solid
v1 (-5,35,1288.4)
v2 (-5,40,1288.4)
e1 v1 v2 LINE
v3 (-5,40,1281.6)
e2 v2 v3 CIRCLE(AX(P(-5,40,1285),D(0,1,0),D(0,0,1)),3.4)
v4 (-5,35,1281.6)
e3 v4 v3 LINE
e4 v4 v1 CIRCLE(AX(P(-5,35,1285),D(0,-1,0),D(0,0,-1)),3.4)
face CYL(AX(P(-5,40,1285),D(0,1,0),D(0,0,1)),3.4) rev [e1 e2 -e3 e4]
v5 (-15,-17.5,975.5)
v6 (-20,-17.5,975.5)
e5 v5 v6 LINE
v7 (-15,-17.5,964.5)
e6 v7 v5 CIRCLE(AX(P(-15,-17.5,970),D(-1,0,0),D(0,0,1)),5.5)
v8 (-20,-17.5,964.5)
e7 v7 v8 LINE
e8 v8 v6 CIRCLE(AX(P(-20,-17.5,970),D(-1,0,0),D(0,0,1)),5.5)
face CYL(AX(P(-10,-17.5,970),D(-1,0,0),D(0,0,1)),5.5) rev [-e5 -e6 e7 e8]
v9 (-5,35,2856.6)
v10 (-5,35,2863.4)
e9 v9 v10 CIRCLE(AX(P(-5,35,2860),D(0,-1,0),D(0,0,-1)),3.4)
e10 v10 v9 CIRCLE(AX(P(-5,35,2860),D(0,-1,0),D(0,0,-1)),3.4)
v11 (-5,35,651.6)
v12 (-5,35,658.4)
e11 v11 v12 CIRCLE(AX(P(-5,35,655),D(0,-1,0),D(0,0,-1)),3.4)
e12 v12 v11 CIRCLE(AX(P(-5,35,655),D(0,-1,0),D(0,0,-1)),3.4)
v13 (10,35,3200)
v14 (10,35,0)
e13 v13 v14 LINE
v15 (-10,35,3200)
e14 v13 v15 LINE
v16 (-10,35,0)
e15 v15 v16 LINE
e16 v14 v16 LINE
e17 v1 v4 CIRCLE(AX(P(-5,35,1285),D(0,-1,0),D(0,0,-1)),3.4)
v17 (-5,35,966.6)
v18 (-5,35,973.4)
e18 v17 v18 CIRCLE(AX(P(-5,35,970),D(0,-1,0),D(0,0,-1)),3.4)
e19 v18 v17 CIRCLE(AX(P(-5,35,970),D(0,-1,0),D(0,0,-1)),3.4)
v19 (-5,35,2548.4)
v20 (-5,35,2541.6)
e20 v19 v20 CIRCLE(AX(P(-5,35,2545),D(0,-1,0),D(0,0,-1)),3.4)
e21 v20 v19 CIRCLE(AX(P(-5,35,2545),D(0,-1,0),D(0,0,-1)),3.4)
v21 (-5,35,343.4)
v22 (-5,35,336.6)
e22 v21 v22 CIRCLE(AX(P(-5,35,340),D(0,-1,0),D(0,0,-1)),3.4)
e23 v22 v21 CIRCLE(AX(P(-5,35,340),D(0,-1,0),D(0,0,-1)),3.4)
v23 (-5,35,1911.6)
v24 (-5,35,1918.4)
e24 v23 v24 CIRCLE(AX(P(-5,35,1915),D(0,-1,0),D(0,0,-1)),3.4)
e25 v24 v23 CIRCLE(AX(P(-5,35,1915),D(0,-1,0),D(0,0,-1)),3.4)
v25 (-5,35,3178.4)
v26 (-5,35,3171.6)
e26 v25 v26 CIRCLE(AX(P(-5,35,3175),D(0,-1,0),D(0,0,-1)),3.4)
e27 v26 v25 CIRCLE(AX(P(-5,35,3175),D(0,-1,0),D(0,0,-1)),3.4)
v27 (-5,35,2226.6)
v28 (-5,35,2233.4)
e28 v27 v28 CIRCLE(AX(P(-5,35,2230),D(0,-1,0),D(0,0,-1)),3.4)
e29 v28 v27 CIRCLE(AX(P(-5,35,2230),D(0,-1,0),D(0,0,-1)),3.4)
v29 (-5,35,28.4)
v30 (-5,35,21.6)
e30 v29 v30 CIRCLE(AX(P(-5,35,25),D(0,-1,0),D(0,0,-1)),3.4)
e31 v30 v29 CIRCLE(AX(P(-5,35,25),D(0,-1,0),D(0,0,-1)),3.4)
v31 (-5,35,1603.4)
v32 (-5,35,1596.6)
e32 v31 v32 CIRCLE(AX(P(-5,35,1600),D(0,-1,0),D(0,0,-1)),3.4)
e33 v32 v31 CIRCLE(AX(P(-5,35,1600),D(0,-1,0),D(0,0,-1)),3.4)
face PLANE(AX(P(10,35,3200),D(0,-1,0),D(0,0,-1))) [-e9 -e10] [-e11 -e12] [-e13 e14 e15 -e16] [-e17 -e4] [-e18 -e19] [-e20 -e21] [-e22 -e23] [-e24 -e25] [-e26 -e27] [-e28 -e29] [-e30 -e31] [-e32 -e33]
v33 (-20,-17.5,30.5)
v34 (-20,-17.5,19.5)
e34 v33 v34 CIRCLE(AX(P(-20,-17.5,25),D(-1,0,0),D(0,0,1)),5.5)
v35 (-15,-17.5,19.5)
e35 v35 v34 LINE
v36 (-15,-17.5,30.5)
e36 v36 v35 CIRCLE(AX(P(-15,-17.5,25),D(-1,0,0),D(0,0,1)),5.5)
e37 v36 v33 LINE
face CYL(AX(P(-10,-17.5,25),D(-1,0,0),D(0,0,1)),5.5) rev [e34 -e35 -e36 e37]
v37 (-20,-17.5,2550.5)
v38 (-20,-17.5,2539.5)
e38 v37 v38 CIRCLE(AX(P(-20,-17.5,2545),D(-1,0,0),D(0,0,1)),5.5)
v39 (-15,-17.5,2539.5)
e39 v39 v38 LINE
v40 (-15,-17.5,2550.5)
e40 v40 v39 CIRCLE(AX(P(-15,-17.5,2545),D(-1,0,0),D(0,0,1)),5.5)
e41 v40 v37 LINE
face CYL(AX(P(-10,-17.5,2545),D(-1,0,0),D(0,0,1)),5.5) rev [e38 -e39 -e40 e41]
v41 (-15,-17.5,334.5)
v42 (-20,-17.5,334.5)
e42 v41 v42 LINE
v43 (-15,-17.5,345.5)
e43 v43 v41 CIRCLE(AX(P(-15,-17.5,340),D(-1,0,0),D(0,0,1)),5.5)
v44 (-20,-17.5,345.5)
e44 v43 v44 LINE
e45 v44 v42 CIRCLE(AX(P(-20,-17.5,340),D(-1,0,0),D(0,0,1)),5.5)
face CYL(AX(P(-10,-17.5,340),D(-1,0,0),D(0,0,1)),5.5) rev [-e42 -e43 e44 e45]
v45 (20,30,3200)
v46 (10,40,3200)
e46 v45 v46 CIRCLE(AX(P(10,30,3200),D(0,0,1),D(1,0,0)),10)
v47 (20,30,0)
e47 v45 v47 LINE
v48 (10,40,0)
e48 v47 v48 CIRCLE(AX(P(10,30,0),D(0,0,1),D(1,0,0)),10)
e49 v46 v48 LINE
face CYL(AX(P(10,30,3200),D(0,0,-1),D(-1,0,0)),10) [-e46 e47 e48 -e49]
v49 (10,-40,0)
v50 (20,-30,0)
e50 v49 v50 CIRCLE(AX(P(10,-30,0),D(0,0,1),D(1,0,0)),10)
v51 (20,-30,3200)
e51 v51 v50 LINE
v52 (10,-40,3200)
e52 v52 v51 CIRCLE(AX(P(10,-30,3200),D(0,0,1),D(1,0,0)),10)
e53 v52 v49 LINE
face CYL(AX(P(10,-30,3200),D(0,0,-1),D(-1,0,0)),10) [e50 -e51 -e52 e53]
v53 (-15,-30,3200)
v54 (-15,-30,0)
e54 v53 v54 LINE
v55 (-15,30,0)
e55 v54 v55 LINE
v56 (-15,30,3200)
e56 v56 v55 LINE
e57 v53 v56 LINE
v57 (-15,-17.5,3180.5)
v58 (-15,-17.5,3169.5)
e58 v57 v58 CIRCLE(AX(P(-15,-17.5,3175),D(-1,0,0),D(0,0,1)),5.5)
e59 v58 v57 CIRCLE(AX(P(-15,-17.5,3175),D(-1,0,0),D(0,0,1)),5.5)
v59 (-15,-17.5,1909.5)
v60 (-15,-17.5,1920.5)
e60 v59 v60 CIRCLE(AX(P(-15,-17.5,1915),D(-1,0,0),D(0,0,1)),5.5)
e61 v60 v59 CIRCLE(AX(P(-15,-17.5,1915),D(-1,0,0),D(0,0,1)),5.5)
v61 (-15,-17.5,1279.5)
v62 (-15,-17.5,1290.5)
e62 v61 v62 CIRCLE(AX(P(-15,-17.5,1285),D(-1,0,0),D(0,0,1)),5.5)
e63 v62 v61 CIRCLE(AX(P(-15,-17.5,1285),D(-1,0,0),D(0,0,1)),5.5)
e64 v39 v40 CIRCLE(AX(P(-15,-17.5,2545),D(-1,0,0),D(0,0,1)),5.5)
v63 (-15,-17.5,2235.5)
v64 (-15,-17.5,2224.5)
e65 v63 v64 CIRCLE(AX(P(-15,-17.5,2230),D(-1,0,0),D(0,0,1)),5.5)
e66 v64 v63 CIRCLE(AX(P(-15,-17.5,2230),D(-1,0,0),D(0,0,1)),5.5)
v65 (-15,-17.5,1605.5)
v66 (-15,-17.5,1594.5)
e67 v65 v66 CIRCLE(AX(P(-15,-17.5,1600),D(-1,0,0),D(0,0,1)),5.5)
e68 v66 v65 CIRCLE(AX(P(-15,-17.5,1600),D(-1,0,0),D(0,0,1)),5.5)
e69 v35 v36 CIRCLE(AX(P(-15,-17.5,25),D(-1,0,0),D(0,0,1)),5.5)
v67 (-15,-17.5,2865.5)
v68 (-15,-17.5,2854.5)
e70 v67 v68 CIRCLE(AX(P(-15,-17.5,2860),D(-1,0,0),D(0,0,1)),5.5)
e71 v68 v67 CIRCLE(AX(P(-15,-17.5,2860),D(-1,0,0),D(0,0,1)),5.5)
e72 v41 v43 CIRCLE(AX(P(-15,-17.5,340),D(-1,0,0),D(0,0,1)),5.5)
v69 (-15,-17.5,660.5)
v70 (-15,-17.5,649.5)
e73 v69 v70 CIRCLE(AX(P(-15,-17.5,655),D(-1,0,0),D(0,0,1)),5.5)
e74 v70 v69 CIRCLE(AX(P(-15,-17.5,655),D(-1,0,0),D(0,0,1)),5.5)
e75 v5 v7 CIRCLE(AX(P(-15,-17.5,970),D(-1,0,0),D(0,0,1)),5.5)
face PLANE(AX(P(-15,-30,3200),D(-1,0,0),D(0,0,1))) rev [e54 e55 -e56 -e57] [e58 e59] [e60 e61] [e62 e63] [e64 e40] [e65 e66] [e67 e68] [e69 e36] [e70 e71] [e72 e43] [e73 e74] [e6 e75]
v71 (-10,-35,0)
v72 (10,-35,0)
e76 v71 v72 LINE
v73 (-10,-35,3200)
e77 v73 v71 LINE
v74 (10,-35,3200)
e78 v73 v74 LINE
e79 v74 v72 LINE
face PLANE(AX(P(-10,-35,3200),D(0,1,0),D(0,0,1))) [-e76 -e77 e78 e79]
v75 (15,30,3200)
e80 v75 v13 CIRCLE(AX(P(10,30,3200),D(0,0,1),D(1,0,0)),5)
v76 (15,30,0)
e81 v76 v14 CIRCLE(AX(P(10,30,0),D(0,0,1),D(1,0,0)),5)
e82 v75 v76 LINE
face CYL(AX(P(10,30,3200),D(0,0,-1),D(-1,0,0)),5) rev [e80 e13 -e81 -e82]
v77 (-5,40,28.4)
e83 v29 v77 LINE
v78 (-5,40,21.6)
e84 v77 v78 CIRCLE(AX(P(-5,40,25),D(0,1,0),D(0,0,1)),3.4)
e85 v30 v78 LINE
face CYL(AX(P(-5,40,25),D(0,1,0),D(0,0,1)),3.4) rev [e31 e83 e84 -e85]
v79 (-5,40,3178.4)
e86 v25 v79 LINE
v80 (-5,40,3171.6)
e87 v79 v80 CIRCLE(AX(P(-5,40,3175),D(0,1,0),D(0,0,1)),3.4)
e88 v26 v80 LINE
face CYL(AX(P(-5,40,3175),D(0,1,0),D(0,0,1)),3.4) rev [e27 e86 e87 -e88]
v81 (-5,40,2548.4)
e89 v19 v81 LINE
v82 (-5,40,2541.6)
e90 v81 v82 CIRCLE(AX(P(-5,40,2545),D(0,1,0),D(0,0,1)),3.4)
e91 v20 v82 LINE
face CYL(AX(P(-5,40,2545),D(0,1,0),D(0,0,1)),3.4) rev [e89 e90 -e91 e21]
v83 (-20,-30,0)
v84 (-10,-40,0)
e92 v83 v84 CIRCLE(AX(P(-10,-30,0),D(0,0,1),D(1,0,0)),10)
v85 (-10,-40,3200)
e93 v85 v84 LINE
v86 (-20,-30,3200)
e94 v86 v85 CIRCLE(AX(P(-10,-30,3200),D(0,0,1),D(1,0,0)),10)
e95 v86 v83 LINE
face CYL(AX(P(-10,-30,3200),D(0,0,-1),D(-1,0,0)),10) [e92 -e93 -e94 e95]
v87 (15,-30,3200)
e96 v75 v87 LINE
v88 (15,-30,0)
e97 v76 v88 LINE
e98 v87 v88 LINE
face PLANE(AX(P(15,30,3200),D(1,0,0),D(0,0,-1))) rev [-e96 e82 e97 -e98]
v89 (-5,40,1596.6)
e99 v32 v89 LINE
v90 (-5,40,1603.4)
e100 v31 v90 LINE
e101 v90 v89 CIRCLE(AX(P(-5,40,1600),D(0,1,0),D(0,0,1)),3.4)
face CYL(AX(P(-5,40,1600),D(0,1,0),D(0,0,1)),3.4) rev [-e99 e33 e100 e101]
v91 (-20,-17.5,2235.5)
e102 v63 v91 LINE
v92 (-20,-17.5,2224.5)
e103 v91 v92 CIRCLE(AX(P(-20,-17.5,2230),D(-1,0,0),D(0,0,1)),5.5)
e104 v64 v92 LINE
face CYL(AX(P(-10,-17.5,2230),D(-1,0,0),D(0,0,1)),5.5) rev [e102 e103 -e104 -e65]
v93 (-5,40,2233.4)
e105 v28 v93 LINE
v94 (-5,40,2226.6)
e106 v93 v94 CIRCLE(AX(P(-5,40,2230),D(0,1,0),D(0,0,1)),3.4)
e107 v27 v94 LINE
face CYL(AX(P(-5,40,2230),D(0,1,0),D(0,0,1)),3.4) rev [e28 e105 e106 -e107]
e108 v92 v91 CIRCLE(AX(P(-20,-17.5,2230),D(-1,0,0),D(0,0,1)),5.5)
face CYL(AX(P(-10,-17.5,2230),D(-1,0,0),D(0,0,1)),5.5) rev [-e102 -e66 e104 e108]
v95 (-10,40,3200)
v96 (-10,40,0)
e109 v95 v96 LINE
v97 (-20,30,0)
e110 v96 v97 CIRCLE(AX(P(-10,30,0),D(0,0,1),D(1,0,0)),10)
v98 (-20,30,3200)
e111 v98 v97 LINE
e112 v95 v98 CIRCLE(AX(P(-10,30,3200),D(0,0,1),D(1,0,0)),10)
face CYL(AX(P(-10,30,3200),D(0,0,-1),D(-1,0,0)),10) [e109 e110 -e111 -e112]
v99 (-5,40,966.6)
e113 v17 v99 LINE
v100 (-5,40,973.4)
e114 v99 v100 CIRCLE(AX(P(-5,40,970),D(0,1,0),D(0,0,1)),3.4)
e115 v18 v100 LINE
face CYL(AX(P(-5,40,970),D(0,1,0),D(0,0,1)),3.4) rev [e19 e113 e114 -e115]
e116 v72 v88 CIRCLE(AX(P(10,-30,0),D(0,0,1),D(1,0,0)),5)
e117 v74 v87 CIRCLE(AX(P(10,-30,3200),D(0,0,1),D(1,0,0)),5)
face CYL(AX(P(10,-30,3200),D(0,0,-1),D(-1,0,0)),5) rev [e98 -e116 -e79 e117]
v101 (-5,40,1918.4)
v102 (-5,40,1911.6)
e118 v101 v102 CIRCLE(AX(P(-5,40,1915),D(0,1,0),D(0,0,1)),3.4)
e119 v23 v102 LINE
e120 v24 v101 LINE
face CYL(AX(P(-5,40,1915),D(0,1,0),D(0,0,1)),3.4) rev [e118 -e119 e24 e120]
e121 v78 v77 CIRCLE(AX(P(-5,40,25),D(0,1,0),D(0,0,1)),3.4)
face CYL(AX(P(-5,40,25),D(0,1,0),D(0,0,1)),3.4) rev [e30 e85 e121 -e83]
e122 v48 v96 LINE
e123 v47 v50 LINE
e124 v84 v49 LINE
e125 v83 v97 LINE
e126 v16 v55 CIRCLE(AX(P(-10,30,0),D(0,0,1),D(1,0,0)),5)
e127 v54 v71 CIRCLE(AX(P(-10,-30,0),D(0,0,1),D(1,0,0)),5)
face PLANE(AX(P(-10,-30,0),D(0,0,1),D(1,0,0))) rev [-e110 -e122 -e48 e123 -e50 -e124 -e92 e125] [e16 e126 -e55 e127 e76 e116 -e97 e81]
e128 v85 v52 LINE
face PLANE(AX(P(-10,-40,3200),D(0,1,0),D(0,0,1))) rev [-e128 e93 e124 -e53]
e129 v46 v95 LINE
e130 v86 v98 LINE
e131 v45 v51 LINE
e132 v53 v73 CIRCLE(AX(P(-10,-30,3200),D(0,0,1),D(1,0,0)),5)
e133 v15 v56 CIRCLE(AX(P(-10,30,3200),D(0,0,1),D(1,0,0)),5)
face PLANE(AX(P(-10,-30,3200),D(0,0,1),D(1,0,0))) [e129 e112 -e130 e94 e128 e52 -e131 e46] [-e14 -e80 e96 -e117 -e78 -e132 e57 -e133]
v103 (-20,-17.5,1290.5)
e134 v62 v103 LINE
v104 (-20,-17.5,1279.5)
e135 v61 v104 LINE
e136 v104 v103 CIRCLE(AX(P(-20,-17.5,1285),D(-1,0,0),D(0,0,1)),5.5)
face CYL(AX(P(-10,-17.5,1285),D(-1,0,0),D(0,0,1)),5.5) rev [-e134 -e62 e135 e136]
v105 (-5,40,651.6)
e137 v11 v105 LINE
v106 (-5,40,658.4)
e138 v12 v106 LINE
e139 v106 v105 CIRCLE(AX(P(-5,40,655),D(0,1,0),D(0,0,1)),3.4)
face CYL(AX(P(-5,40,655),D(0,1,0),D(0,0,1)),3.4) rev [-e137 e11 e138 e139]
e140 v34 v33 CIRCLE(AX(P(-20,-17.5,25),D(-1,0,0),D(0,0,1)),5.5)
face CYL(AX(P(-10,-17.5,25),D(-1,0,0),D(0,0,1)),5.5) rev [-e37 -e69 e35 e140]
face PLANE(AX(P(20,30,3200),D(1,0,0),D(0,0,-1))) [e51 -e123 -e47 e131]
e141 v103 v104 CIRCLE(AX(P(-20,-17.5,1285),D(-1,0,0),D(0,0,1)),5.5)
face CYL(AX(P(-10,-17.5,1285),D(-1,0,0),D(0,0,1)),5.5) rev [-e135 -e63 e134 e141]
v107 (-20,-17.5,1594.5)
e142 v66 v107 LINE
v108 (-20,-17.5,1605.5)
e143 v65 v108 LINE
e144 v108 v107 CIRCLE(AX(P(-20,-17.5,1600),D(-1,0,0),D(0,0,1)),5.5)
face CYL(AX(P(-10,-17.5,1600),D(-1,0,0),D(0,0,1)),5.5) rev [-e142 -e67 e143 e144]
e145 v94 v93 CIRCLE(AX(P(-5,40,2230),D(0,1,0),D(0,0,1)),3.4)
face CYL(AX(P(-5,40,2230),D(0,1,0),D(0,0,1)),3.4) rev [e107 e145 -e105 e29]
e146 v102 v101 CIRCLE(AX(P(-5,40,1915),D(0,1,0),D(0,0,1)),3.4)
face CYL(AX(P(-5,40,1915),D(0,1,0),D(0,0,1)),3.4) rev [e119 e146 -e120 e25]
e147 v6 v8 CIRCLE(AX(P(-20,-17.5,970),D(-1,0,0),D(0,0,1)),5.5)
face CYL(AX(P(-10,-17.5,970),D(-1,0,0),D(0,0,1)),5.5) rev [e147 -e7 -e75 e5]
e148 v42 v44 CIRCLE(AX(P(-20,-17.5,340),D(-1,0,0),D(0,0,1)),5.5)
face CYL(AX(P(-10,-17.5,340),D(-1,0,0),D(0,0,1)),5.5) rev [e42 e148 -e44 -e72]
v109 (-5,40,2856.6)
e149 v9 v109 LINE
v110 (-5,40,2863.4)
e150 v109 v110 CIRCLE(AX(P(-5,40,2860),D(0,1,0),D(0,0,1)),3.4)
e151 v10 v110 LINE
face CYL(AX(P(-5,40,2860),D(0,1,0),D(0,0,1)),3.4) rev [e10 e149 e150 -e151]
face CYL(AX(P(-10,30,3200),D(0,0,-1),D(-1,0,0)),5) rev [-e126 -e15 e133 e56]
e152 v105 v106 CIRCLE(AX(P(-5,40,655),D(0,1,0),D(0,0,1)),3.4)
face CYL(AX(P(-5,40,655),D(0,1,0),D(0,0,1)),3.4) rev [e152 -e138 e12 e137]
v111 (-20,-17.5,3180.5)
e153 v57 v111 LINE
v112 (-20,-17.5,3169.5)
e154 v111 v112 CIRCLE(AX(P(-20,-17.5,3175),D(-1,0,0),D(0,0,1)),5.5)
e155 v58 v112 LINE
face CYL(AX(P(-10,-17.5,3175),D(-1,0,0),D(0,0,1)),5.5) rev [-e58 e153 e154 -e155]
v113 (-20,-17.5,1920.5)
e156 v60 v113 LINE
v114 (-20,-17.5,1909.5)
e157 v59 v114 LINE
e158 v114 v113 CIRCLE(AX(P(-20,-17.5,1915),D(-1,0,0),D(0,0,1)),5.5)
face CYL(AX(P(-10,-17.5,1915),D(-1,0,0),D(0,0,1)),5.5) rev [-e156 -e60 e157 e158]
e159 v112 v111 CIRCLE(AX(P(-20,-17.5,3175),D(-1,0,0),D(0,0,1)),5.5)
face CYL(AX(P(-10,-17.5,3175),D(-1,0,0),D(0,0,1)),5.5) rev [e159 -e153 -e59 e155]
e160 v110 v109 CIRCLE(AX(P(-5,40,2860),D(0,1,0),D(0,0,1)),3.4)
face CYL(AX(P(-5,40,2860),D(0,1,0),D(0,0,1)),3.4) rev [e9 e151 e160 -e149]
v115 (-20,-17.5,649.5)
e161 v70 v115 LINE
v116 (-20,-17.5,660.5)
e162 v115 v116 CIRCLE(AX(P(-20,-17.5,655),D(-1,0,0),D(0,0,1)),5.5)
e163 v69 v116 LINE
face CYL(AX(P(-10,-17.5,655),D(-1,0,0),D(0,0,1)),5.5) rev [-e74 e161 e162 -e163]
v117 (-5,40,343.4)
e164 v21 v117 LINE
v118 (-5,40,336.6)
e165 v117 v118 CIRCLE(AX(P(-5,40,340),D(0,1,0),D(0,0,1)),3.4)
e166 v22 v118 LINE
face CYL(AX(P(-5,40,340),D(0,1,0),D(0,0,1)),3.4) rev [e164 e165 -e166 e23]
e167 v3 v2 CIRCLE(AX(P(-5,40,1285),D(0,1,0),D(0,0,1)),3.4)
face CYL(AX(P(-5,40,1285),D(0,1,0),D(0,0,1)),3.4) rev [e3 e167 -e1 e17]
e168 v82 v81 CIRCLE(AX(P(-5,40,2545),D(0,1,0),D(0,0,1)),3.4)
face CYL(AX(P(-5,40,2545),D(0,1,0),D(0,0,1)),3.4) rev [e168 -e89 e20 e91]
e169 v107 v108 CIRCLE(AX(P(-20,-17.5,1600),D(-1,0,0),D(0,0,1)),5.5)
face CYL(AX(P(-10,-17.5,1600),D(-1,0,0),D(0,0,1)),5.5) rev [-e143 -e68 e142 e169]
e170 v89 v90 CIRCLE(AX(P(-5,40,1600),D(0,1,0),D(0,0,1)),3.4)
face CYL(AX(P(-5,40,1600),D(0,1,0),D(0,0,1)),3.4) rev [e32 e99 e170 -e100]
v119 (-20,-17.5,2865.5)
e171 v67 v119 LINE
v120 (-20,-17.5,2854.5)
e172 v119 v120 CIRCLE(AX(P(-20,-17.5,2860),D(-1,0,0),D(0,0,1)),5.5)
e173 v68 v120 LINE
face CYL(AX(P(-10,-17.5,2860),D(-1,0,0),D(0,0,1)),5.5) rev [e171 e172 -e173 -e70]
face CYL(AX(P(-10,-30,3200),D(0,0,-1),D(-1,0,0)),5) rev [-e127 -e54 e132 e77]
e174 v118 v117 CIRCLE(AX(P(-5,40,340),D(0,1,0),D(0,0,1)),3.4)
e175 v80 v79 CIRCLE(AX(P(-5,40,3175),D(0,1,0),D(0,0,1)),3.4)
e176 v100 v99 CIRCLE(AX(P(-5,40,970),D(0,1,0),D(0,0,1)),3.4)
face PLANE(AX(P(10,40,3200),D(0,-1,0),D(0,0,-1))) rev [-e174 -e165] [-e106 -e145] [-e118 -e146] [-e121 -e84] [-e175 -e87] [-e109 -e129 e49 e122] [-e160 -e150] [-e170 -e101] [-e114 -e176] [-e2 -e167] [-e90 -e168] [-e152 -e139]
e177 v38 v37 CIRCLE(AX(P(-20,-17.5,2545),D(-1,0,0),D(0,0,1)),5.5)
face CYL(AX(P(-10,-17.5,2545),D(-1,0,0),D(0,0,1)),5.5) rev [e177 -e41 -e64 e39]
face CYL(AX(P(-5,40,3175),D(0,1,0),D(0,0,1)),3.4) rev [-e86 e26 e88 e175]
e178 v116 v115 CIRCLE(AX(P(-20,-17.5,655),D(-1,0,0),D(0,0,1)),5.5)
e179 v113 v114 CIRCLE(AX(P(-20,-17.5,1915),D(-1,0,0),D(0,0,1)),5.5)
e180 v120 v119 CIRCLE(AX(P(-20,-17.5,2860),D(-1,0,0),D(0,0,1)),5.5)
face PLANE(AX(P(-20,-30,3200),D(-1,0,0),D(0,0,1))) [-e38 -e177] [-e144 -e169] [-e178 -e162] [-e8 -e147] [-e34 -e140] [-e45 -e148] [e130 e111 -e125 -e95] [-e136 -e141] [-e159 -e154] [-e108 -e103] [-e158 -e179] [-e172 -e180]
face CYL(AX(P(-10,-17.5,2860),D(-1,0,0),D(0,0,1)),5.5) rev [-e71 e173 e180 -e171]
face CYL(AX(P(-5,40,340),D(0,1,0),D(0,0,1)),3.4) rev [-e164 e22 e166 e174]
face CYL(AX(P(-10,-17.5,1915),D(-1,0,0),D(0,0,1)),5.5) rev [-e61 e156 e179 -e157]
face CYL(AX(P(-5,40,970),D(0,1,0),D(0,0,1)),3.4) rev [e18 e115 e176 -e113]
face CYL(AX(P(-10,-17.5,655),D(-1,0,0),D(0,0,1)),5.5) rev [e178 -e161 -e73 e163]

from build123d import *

# Parameters (mm, degrees)
BOSS_EXTRUDE1_DEPTH   = 3200
SKETCH_1_R            = 3.25
CUT_EXTRUDE1_DEPTH    = 10
M8_TAPPED_HOLE1_D     = 6.8
M8_TAPPED_HOLE1_DEPTH = 22.25
M8_TAPPED_HOLE1_TIP   = 2.042926105
SKETCH9_R             = 5.5
CUT_EXTRUDE2_DEPTH    = 10
LPATTERN1_COUNT       = 11
LPATTERN1_PITCH       = 315


with BuildPart() as part:
    # Sketch1 → Boss-Extrude1 (new body)
    with BuildSketch(Plane.XY):
        with BuildLine():
            Line((-10, -40), (10, -40))
            ThreePointArc((10, -40), (17.071067812, -37.071067812), (20, -30))
            Line((20, -30), (20, 30))
            ThreePointArc((20, 30), (17.071067812, 37.071067812), (10, 40))
            Line((10, 40), (-10, 40))
            ThreePointArc((-10, 40), (-17.071067812, 37.071067812), (-20, 30))
            Line((-20, 30), (-20, -30))
            ThreePointArc((-20, -30), (-17.071067812, -37.071067812), (-10, -40))
        make_face()
        with BuildLine():
            Line((-10, -35), (10, -35))
            ThreePointArc((10, -35), (13.535533906, -33.535533906), (15, -30))
            Line((15, -30), (15, 30))
            ThreePointArc((15, 30), (13.535533906, 33.535533906), (10, 35))
            Line((10, 35), (-10, 35))
            ThreePointArc((-10, 35), (-13.535533906, 33.535533906), (-15, 30))
            Line((-15, 30), (-15, -30))
            ThreePointArc((-15, -30), (-13.535533906, -33.535533906), (-10, -35))
        make_face(mode=Mode.SUBTRACT)
    extrude(amount=BOSS_EXTRUDE1_DEPTH)

    # 草图1 → Cut-Extrude1 (cut)
    with BuildSketch(Plane(origin=(0, 40, 0), x_dir=(1, 0, 0), z_dir=(0, 1, 0))):
        with Locations(Location((-5, -3175, 0), (0, 0, 270))):
            Circle(SKETCH_1_R)
        with Locations(Location((-5, -2860, 0), (0, 0, 270))):
            Circle(SKETCH_1_R)
        with Locations(Location((-5, -2545, 0), (0, 0, 270))):
            Circle(SKETCH_1_R)
        with Locations(Location((-5, -2230, 0), (0, 0, 270))):
            Circle(SKETCH_1_R)
        with Locations(Location((-5, -1915, 0), (0, 0, 270))):
            Circle(SKETCH_1_R)
        with Locations(Location((-5, -1600, 0), (0, 0, 270))):
            Circle(SKETCH_1_R)
        with Locations(Location((-5, -1285, 0), (0, 0, 270))):
            Circle(SKETCH_1_R)
        with Locations(Location((-5, -970, 0), (0, 0, 270))):
            Circle(SKETCH_1_R)
        with Locations(Location((-5, -655, 0), (0, 0, 270))):
            Circle(SKETCH_1_R)
        with Locations(Location((-5, -340, 0), (0, 0, 270))):
            Circle(SKETCH_1_R)
        with Locations(Location((-5, -25, 0), (0, 0, 270))):
            Circle(SKETCH_1_R)
    extrude(amount=-CUT_EXTRUDE1_DEPTH, mode=Mode.SUBTRACT)

    # M8 Tapped Hole1
    with Locations(Plane(origin=(0, 40, 0), x_dir=(1, 0, 0), z_dir=(0, 1, 0))):
        with Locations((-5, -3175), (-5, -2860), (-5, -2545), (-5, -2230), (-5, -1915), (-5, -1600), (-5, -1285), (-5, -970), (-5, -655), (-5, -340), (-5, -25)):
            Hole(M8_TAPPED_HOLE1_D / 2, depth=M8_TAPPED_HOLE1_DEPTH)
            with Locations((0, 0, -(M8_TAPPED_HOLE1_DEPTH + M8_TAPPED_HOLE1_TIP / 2))):  # 118° drill point
                Cone(0, M8_TAPPED_HOLE1_D / 2, M8_TAPPED_HOLE1_TIP, mode=Mode.SUBTRACT)

    # Sketch9 → Cut-Extrude2 (cut)
    with BuildSketch(Plane.ZY.offset(20)):
        with Locations((25, -17.5)):
            Circle(SKETCH9_R)
    cut_extrude2 = extrude(amount=-CUT_EXTRUDE2_DEPTH, mode=Mode.SUBTRACT)

    # LPattern1: Cut-Extrude2 ×11
    with Locations(*[(0, 0, i * LPATTERN1_PITCH) for i in range(1, LPATTERN1_COUNT)]):
        add(cut_extrude2, mode=Mode.SUBTRACT)


solid = part.part
